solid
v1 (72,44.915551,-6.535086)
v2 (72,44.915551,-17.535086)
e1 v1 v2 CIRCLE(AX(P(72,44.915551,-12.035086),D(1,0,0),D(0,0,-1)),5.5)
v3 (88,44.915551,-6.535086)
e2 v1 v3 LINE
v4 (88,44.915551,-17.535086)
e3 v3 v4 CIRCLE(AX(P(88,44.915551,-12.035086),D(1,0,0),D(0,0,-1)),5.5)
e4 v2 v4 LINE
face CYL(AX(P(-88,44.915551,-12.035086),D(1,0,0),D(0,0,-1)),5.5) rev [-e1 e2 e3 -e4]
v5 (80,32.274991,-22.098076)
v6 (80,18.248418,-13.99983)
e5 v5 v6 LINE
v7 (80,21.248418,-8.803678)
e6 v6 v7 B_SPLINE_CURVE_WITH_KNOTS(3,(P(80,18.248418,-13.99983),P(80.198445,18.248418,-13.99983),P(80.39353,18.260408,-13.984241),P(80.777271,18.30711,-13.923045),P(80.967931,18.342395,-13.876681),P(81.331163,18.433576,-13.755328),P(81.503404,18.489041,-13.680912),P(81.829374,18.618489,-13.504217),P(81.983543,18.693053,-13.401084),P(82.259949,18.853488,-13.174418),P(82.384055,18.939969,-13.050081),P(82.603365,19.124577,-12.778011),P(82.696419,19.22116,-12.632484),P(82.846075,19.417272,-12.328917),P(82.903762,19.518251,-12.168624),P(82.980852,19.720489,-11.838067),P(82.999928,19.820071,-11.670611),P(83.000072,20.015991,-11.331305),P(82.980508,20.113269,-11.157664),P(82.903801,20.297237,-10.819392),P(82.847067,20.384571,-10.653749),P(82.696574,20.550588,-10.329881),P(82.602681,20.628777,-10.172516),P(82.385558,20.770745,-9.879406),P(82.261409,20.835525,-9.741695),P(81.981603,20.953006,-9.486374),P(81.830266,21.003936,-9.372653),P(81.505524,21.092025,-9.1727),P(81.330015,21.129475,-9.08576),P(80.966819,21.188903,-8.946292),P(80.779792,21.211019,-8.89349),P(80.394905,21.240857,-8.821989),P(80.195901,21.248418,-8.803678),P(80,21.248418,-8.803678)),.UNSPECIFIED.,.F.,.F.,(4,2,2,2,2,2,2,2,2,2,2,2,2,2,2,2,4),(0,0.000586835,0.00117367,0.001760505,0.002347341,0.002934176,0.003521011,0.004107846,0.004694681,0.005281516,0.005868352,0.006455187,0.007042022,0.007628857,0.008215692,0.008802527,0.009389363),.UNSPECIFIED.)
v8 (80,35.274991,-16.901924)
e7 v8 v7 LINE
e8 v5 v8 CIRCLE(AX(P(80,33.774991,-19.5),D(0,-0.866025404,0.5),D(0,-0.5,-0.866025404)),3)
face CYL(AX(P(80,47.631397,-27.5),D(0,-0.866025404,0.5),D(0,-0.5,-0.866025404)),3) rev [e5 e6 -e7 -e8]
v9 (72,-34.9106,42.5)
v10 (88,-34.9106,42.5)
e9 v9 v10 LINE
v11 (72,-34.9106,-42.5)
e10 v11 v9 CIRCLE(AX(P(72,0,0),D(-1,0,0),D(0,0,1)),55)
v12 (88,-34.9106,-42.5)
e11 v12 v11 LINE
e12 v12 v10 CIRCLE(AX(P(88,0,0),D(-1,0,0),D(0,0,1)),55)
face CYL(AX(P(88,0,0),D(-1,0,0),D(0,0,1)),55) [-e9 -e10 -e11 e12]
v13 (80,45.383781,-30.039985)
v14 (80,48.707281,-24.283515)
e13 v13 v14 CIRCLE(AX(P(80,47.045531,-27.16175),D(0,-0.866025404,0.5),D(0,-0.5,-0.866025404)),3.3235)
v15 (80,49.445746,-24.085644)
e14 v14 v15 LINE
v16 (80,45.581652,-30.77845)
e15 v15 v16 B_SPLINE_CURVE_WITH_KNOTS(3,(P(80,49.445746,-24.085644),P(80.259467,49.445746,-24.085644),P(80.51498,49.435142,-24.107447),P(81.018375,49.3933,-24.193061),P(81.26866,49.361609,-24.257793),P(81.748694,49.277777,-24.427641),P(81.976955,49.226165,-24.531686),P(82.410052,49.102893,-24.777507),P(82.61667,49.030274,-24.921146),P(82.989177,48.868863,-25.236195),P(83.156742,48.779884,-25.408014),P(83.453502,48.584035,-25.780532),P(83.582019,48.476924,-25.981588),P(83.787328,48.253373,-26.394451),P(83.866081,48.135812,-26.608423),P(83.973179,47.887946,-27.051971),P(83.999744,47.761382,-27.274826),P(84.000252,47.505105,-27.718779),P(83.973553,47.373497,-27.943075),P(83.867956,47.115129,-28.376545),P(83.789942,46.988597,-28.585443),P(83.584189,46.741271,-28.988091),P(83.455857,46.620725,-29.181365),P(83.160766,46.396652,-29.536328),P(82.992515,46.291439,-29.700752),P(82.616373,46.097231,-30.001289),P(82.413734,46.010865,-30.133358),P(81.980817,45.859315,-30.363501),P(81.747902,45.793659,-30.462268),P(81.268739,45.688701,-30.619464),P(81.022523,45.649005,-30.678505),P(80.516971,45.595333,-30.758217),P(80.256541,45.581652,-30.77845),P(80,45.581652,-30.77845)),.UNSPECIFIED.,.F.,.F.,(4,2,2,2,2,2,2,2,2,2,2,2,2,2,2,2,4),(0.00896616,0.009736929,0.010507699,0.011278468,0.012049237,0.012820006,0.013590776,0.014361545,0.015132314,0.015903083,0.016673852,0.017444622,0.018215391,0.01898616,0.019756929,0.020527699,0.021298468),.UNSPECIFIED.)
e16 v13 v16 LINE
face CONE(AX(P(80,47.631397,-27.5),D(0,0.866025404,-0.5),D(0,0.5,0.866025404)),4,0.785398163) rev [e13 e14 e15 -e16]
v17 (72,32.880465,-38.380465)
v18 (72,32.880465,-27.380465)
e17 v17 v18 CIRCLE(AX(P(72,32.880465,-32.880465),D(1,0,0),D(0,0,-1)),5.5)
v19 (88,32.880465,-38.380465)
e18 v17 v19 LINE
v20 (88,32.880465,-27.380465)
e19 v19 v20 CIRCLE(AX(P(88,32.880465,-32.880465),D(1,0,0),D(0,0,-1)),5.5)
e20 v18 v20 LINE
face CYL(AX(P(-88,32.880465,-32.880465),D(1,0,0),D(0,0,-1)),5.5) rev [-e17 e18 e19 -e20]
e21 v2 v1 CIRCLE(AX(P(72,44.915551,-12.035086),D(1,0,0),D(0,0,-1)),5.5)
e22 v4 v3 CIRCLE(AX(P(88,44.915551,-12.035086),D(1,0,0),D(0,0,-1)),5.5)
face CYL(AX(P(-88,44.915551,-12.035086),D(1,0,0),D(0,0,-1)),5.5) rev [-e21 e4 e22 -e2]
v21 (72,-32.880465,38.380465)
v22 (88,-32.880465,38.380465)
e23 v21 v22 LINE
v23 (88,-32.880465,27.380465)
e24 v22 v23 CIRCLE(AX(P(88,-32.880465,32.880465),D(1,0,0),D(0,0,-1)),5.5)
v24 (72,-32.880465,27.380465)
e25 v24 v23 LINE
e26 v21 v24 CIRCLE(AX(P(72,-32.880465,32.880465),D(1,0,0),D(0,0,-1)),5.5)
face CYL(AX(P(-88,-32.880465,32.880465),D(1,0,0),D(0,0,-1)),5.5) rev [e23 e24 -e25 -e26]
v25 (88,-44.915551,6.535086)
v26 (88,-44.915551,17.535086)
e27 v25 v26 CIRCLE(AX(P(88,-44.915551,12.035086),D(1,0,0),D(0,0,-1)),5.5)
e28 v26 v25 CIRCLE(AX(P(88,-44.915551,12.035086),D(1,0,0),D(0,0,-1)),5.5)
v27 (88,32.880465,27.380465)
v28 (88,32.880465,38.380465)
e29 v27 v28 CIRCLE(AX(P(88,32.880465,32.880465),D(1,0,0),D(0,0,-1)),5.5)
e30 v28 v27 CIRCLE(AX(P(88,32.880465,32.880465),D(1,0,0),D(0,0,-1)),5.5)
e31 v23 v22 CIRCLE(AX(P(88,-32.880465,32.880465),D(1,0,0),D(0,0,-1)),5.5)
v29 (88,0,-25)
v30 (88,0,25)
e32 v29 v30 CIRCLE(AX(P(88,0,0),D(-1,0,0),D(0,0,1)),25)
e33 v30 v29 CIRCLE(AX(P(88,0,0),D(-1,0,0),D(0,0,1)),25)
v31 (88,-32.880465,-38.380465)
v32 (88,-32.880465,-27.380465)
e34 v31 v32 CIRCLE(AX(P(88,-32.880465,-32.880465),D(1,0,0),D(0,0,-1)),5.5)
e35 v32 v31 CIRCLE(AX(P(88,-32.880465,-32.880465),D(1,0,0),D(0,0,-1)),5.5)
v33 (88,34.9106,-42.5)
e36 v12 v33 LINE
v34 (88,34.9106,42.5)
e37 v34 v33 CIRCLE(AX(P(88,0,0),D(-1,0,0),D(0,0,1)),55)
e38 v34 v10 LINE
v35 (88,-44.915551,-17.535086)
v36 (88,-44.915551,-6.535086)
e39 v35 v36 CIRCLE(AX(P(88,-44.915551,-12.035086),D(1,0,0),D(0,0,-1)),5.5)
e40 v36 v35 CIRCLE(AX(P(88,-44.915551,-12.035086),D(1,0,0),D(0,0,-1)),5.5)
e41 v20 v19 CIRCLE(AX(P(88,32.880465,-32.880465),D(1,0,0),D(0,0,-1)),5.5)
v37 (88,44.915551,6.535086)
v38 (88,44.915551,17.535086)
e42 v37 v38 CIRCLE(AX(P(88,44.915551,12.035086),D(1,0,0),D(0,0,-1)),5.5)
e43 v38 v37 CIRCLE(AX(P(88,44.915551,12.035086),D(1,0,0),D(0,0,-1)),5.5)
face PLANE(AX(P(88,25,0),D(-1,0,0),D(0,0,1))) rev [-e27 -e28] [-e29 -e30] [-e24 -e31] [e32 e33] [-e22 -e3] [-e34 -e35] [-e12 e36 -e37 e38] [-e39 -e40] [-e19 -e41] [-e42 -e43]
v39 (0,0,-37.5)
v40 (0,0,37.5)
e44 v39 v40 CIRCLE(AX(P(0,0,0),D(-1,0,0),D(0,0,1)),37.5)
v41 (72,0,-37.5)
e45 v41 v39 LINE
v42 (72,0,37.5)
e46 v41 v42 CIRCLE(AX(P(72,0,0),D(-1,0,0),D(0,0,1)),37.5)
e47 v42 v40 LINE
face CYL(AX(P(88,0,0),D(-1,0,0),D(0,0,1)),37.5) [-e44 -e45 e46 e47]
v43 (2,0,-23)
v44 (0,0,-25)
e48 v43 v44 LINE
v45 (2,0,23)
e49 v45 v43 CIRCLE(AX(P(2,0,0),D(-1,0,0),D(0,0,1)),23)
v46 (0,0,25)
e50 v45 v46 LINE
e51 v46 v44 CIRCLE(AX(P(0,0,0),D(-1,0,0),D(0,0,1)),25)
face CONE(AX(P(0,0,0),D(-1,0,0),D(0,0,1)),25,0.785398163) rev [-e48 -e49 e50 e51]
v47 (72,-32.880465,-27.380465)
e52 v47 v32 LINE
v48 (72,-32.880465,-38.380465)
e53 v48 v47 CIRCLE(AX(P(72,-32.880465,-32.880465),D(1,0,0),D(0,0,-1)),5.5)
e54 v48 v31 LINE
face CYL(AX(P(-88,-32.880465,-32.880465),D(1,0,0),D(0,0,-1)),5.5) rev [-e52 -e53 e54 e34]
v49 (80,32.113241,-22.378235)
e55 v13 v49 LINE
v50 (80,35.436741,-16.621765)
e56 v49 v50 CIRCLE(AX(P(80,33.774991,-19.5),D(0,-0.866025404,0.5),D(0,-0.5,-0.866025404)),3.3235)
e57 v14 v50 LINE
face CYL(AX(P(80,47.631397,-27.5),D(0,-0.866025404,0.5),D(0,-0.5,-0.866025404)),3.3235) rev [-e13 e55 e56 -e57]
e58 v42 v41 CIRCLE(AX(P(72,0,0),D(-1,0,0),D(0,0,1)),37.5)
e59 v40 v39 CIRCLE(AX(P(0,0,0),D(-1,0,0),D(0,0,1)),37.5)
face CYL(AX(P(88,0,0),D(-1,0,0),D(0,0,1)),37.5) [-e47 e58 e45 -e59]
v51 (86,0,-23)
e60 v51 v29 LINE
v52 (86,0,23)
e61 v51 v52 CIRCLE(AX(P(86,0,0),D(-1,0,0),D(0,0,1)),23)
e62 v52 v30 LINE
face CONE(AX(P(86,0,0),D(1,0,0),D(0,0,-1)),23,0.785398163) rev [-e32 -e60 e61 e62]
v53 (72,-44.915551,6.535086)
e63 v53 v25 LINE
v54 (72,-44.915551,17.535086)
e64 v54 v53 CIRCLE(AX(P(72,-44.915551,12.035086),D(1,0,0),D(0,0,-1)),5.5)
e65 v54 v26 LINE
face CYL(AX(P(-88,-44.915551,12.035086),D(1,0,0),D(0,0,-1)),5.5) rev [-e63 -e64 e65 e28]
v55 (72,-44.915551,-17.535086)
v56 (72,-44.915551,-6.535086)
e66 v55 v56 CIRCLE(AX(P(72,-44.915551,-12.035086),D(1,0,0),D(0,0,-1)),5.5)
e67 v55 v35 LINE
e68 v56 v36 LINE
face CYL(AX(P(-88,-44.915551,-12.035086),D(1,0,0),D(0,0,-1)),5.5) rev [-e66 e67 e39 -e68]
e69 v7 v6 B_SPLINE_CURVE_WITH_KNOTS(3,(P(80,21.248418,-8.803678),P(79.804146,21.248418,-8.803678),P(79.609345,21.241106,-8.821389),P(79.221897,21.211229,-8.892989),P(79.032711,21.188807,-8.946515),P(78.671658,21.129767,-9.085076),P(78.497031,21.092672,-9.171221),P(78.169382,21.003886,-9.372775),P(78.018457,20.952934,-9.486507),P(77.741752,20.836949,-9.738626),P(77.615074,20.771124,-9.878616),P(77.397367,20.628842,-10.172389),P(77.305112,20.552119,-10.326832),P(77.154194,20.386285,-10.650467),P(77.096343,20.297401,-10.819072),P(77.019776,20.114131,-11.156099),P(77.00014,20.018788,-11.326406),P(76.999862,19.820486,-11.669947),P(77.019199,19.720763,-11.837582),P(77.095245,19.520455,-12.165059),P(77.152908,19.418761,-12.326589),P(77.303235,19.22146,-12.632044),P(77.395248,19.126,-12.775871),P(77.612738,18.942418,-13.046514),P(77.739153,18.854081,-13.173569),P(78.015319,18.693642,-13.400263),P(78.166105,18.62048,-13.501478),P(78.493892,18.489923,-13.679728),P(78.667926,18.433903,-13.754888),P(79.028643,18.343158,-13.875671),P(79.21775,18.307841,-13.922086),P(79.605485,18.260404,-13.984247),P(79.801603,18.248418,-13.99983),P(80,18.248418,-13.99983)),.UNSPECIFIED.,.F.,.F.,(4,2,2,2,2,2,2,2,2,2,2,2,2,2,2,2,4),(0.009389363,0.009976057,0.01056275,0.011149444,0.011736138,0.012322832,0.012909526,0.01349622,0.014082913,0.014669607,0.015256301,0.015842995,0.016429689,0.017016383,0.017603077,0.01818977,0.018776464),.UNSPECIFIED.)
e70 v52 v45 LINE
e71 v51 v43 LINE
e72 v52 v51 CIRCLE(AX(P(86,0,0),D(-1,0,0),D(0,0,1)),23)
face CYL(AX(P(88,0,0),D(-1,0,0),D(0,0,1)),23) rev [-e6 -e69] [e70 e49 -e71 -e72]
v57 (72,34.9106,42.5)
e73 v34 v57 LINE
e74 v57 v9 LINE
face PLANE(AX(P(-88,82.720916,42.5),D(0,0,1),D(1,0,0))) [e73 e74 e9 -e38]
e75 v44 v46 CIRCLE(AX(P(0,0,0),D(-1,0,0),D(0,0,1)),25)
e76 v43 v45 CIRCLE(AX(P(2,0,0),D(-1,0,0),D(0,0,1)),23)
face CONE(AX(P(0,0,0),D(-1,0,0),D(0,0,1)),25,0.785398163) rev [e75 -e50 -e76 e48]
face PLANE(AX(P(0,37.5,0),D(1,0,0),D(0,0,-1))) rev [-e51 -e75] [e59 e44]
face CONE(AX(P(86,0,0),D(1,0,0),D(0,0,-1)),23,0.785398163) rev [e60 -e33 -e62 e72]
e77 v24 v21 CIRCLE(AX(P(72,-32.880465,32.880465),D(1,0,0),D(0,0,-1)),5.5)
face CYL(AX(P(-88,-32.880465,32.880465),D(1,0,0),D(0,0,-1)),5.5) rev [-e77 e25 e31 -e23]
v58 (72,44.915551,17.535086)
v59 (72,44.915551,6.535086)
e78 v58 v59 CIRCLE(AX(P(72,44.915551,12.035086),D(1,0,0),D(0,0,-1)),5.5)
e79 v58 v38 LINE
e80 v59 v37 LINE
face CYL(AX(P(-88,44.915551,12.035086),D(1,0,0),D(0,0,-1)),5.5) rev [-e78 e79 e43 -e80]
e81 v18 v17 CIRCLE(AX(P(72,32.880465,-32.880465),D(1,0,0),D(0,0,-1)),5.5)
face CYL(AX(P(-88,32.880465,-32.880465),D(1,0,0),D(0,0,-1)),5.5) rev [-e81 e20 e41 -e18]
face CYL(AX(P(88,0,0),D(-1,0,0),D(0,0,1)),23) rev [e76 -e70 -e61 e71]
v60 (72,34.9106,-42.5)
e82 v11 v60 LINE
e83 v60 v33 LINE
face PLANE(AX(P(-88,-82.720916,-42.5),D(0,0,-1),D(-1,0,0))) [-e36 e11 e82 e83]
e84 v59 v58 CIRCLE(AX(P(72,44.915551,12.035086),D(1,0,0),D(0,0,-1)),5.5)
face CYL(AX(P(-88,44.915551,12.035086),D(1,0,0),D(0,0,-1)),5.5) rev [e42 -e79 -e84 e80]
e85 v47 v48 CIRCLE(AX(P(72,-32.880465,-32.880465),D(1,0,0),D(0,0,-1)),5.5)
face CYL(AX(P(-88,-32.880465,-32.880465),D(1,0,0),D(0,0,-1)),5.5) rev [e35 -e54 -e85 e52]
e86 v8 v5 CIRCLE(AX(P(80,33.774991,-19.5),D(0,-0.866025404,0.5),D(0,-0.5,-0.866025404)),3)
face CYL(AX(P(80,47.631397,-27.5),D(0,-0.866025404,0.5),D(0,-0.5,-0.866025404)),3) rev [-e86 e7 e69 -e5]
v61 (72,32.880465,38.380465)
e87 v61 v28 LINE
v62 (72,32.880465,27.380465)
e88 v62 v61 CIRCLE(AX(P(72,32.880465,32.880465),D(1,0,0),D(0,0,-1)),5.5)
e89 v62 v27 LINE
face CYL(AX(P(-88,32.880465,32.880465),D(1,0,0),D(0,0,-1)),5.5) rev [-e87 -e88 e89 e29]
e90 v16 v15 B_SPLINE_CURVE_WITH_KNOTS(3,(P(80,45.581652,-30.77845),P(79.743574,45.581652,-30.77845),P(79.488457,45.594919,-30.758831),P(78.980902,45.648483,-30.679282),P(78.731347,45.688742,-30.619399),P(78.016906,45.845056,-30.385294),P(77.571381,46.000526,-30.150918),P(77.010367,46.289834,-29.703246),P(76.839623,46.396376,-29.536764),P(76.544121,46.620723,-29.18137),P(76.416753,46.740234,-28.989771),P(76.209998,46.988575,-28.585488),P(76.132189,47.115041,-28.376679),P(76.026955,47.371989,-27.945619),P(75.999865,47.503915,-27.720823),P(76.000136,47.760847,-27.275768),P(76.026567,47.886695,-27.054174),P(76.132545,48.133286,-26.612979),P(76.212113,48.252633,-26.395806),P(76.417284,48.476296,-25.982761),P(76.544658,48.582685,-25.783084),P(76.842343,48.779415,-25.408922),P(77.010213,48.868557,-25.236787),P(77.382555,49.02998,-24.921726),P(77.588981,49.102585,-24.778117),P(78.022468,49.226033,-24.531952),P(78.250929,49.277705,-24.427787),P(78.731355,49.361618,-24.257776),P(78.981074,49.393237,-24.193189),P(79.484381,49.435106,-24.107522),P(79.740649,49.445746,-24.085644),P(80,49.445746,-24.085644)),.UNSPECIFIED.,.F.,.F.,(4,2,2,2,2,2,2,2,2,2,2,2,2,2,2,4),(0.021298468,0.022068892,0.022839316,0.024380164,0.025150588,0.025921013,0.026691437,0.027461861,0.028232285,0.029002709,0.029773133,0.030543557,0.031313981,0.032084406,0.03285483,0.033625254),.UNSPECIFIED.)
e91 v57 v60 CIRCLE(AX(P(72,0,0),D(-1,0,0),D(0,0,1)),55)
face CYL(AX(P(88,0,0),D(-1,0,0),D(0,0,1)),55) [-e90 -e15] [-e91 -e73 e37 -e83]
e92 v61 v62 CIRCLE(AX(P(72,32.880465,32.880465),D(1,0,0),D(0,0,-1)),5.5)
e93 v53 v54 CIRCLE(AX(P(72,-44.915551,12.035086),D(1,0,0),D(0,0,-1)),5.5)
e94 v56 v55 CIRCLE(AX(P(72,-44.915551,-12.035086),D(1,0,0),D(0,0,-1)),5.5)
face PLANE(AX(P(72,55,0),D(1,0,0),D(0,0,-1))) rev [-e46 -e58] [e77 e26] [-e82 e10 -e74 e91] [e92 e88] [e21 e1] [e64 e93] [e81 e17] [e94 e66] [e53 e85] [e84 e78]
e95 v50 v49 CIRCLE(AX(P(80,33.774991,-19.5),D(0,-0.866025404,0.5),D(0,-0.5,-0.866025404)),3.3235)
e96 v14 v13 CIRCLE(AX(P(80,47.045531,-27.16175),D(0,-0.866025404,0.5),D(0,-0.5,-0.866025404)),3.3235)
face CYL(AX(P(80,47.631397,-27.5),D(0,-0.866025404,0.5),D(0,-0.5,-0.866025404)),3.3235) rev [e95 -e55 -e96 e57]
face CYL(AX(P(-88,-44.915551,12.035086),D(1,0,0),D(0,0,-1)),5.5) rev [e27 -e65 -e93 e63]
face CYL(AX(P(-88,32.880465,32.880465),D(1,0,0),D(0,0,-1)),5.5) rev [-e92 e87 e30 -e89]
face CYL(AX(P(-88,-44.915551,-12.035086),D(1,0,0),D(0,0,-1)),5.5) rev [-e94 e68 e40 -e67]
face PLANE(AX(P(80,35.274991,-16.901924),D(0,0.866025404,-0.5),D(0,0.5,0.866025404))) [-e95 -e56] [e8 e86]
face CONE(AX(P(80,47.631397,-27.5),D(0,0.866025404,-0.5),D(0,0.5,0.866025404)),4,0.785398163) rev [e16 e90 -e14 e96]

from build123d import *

# Parameters (mm, degrees)
CUT_EXTRUDE_1_DEPTH      = 88
CUT_EXTRUDE_1_DEPTH_BACK = 88
SKETCH_2_R               = 105
CUT_EXTRUDE_2_DEPTH      = 88
CUT_EXTRUDE_2_DEPTH_BACK = 88
SKETCH_3_R               = 5.5
CUT_EXTRUDE_3_DEPTH      = 88
CUT_EXTRUDE_3_DEPTH_BACK = 88
SKETCH_5_R               = 5.5
CUT_EXTRUDE_4_DEPTH      = 88
CUT_EXTRUDE_4_DEPTH_BACK = 88
SKETCH_6_R               = 5.5
CUT_EXTRUDE_5_DEPTH      = 88
CUT_EXTRUDE_5_DEPTH_BACK = 88
SKETCH_7_R               = 5.5
CUT_EXTRUDE_6_DEPTH      = 88
CUT_EXTRUDE_6_DEPTH_BACK = 88
SKETCH_8_R               = 5.5
CUT_EXTRUDE_7_DEPTH      = 88
CUT_EXTRUDE_7_DEPTH_BACK = 88
SKETCH_9_R               = 5.5
CUT_EXTRUDE_8_DEPTH      = 88
CUT_EXTRUDE_8_DEPTH_BACK = 88
SKETCH_10_R              = 5.5
CUT_EXTRUDE_9_DEPTH      = 88
CUT_EXTRUDE_9_DEPTH_BACK = 88
SKETCH_11_R              = 5.5


with BuildPart() as part:
    # 草图1 → 旋转1 (revolve)
    with BuildSketch(Plane.XY, mode=Mode.PRIVATE) as revolve_1_sk:
        Polygon((0, 37.5), (0, 25), (2, 23), (86, 23), (88, 25), (88, 55), (72, 55), (72, 37.5), align=None)
    revolve(revolve_1_sk.sketch.rotate(Axis((88, 0, 0), (-1, 0, 0)), 270), axis=Axis((88, 0, 0), (-1, 0, 0)))

    # 草图2 → 切除-拉伸1 (cut, two sides: drawn at the far end of the back side and taken through both)
    with BuildSketch(Plane(origin=(0, 0, 0), x_dir=(0, 0, -1), z_dir=(1, 0, 0)).offset(-CUT_EXTRUDE_1_DEPTH_BACK)):
        Circle(SKETCH_2_R)
        with BuildLine():
            Line((-42.5, 82.720916339), (-42.5, -82.720916339))
            ThreePointArc((-42.5, -82.720916339), (0, -93), (42.5, -82.720916339))
            Line((42.5, -82.720916339), (42.5, 82.720916339))
            ThreePointArc((42.5, 82.720916339), (0, 93), (-42.5, 82.720916339))
        make_face(mode=Mode.SUBTRACT)
    extrude(amount=CUT_EXTRUDE_1_DEPTH + CUT_EXTRUDE_1_DEPTH_BACK, mode=Mode.SUBTRACT)

    # 草图3 → 切除-拉伸2 (cut, two sides: drawn at the far end of the back side and taken through both)
    with BuildSketch(Plane(origin=(0, 0, 0), x_dir=(0, 0, -1), z_dir=(1, 0, 0)).offset(-CUT_EXTRUDE_2_DEPTH_BACK)):
        with Locations((-32.880465325, 32.880465325)):
            Circle(SKETCH_3_R)
    extrude(amount=CUT_EXTRUDE_2_DEPTH + CUT_EXTRUDE_2_DEPTH_BACK, mode=Mode.SUBTRACT)

    # 草图5 → 切除-拉伸3 (cut, two sides: drawn at the far end of the back side and taken through both)
    with BuildSketch(Plane(origin=(0, 0, 0), x_dir=(0, 0, -1), z_dir=(1, 0, 0)).offset(-CUT_EXTRUDE_3_DEPTH_BACK)):
        with Locations((-12.035085597, 44.915550922)):
            Circle(SKETCH_5_R)
    extrude(amount=CUT_EXTRUDE_3_DEPTH + CUT_EXTRUDE_3_DEPTH_BACK, mode=Mode.SUBTRACT)

    # 草图6 → 切除-拉伸4 (cut, two sides: drawn at the far end of the back side and taken through both)
    with BuildSketch(Plane(origin=(0, 0, 0), x_dir=(0, 0, -1), z_dir=(1, 0, 0)).offset(-CUT_EXTRUDE_4_DEPTH_BACK)):
        with Locations((12.035085597, 44.915550922)):
            Circle(SKETCH_6_R)
    extrude(amount=CUT_EXTRUDE_4_DEPTH + CUT_EXTRUDE_4_DEPTH_BACK, mode=Mode.SUBTRACT)

    # 草图7 → 切除-拉伸5 (cut, two sides: drawn at the far end of the back side and taken through both)
    with BuildSketch(Plane(origin=(0, 0, 0), x_dir=(0, 0, -1), z_dir=(1, 0, 0)).offset(-CUT_EXTRUDE_5_DEPTH_BACK)):
        with Locations((32.880465325, 32.880465325)):
            Circle(SKETCH_7_R)
    extrude(amount=CUT_EXTRUDE_5_DEPTH + CUT_EXTRUDE_5_DEPTH_BACK, mode=Mode.SUBTRACT)

    # 草图8 → 切除-拉伸6 (cut, two sides: drawn at the far end of the back side and taken through both)
    with BuildSketch(Plane(origin=(0, 0, 0), x_dir=(0, 0, -1), z_dir=(1, 0, 0)).offset(-CUT_EXTRUDE_6_DEPTH_BACK)):
        with Locations((32.880465325, -32.880465325)):
            Circle(SKETCH_8_R)
    extrude(amount=CUT_EXTRUDE_6_DEPTH + CUT_EXTRUDE_6_DEPTH_BACK, mode=Mode.SUBTRACT)

    # 草图9 → 切除-拉伸7 (cut, two sides: drawn at the far end of the back side and taken through both)
    with BuildSketch(Plane(origin=(0, 0, 0), x_dir=(0, 0, -1), z_dir=(1, 0, 0)).offset(-CUT_EXTRUDE_7_DEPTH_BACK)):
        with Locations((12.035085597, -44.915550922)):
            Circle(SKETCH_9_R)
    extrude(amount=CUT_EXTRUDE_7_DEPTH + CUT_EXTRUDE_7_DEPTH_BACK, mode=Mode.SUBTRACT)

    # 草图10 → 切除-拉伸8 (cut, two sides: drawn at the far end of the back side and taken through both)
    with BuildSketch(Plane(origin=(0, 0, 0), x_dir=(0, 0, -1), z_dir=(1, 0, 0)).offset(-CUT_EXTRUDE_8_DEPTH_BACK)):
        with Locations((-12.035085597, -44.915550922)):
            Circle(SKETCH_10_R)
    extrude(amount=CUT_EXTRUDE_8_DEPTH + CUT_EXTRUDE_8_DEPTH_BACK, mode=Mode.SUBTRACT)

    # 草图11 → 切除-拉伸9 (cut, two sides: drawn at the far end of the back side and taken through both)
    with BuildSketch(Plane(origin=(0, 0, 0), x_dir=(0, 0, -1), z_dir=(1, 0, 0)).offset(-CUT_EXTRUDE_9_DEPTH_BACK)):
        with Locations((-32.880465325, -32.880465325)):
            Circle(SKETCH_11_R)
    extrude(amount=CUT_EXTRUDE_9_DEPTH + CUT_EXTRUDE_9_DEPTH_BACK, mode=Mode.SUBTRACT)

    # 草图12 → 切除-旋转1 (revolve, cut)
    with BuildSketch(Plane(origin=(80, 0, 0), x_dir=(0, 0, -1), z_dir=(1, 0, 0)), mode=Mode.PRIVATE) as cut_revolve_1_sk:
        Polygon((7.5, 12.990381057), (4.901923789, 14.490381057), (16.901923789, 35.274990748), (16.621764571, 35.436740748), (24.283514571, 48.707281022), (24.035898385, 49.631397208), (27.5, 47.631397208), align=None)
    revolve(cut_revolve_1_sk.sketch.rotate(Axis((80, 47.631397208, -27.5), (0, -0.8660254037844387, 0.49999999999999983)), 180), axis=Axis((80, 47.631397208, -27.5), (0, -0.8660254037844387, 0.49999999999999983)), mode=Mode.SUBTRACT)


solid = part.part
